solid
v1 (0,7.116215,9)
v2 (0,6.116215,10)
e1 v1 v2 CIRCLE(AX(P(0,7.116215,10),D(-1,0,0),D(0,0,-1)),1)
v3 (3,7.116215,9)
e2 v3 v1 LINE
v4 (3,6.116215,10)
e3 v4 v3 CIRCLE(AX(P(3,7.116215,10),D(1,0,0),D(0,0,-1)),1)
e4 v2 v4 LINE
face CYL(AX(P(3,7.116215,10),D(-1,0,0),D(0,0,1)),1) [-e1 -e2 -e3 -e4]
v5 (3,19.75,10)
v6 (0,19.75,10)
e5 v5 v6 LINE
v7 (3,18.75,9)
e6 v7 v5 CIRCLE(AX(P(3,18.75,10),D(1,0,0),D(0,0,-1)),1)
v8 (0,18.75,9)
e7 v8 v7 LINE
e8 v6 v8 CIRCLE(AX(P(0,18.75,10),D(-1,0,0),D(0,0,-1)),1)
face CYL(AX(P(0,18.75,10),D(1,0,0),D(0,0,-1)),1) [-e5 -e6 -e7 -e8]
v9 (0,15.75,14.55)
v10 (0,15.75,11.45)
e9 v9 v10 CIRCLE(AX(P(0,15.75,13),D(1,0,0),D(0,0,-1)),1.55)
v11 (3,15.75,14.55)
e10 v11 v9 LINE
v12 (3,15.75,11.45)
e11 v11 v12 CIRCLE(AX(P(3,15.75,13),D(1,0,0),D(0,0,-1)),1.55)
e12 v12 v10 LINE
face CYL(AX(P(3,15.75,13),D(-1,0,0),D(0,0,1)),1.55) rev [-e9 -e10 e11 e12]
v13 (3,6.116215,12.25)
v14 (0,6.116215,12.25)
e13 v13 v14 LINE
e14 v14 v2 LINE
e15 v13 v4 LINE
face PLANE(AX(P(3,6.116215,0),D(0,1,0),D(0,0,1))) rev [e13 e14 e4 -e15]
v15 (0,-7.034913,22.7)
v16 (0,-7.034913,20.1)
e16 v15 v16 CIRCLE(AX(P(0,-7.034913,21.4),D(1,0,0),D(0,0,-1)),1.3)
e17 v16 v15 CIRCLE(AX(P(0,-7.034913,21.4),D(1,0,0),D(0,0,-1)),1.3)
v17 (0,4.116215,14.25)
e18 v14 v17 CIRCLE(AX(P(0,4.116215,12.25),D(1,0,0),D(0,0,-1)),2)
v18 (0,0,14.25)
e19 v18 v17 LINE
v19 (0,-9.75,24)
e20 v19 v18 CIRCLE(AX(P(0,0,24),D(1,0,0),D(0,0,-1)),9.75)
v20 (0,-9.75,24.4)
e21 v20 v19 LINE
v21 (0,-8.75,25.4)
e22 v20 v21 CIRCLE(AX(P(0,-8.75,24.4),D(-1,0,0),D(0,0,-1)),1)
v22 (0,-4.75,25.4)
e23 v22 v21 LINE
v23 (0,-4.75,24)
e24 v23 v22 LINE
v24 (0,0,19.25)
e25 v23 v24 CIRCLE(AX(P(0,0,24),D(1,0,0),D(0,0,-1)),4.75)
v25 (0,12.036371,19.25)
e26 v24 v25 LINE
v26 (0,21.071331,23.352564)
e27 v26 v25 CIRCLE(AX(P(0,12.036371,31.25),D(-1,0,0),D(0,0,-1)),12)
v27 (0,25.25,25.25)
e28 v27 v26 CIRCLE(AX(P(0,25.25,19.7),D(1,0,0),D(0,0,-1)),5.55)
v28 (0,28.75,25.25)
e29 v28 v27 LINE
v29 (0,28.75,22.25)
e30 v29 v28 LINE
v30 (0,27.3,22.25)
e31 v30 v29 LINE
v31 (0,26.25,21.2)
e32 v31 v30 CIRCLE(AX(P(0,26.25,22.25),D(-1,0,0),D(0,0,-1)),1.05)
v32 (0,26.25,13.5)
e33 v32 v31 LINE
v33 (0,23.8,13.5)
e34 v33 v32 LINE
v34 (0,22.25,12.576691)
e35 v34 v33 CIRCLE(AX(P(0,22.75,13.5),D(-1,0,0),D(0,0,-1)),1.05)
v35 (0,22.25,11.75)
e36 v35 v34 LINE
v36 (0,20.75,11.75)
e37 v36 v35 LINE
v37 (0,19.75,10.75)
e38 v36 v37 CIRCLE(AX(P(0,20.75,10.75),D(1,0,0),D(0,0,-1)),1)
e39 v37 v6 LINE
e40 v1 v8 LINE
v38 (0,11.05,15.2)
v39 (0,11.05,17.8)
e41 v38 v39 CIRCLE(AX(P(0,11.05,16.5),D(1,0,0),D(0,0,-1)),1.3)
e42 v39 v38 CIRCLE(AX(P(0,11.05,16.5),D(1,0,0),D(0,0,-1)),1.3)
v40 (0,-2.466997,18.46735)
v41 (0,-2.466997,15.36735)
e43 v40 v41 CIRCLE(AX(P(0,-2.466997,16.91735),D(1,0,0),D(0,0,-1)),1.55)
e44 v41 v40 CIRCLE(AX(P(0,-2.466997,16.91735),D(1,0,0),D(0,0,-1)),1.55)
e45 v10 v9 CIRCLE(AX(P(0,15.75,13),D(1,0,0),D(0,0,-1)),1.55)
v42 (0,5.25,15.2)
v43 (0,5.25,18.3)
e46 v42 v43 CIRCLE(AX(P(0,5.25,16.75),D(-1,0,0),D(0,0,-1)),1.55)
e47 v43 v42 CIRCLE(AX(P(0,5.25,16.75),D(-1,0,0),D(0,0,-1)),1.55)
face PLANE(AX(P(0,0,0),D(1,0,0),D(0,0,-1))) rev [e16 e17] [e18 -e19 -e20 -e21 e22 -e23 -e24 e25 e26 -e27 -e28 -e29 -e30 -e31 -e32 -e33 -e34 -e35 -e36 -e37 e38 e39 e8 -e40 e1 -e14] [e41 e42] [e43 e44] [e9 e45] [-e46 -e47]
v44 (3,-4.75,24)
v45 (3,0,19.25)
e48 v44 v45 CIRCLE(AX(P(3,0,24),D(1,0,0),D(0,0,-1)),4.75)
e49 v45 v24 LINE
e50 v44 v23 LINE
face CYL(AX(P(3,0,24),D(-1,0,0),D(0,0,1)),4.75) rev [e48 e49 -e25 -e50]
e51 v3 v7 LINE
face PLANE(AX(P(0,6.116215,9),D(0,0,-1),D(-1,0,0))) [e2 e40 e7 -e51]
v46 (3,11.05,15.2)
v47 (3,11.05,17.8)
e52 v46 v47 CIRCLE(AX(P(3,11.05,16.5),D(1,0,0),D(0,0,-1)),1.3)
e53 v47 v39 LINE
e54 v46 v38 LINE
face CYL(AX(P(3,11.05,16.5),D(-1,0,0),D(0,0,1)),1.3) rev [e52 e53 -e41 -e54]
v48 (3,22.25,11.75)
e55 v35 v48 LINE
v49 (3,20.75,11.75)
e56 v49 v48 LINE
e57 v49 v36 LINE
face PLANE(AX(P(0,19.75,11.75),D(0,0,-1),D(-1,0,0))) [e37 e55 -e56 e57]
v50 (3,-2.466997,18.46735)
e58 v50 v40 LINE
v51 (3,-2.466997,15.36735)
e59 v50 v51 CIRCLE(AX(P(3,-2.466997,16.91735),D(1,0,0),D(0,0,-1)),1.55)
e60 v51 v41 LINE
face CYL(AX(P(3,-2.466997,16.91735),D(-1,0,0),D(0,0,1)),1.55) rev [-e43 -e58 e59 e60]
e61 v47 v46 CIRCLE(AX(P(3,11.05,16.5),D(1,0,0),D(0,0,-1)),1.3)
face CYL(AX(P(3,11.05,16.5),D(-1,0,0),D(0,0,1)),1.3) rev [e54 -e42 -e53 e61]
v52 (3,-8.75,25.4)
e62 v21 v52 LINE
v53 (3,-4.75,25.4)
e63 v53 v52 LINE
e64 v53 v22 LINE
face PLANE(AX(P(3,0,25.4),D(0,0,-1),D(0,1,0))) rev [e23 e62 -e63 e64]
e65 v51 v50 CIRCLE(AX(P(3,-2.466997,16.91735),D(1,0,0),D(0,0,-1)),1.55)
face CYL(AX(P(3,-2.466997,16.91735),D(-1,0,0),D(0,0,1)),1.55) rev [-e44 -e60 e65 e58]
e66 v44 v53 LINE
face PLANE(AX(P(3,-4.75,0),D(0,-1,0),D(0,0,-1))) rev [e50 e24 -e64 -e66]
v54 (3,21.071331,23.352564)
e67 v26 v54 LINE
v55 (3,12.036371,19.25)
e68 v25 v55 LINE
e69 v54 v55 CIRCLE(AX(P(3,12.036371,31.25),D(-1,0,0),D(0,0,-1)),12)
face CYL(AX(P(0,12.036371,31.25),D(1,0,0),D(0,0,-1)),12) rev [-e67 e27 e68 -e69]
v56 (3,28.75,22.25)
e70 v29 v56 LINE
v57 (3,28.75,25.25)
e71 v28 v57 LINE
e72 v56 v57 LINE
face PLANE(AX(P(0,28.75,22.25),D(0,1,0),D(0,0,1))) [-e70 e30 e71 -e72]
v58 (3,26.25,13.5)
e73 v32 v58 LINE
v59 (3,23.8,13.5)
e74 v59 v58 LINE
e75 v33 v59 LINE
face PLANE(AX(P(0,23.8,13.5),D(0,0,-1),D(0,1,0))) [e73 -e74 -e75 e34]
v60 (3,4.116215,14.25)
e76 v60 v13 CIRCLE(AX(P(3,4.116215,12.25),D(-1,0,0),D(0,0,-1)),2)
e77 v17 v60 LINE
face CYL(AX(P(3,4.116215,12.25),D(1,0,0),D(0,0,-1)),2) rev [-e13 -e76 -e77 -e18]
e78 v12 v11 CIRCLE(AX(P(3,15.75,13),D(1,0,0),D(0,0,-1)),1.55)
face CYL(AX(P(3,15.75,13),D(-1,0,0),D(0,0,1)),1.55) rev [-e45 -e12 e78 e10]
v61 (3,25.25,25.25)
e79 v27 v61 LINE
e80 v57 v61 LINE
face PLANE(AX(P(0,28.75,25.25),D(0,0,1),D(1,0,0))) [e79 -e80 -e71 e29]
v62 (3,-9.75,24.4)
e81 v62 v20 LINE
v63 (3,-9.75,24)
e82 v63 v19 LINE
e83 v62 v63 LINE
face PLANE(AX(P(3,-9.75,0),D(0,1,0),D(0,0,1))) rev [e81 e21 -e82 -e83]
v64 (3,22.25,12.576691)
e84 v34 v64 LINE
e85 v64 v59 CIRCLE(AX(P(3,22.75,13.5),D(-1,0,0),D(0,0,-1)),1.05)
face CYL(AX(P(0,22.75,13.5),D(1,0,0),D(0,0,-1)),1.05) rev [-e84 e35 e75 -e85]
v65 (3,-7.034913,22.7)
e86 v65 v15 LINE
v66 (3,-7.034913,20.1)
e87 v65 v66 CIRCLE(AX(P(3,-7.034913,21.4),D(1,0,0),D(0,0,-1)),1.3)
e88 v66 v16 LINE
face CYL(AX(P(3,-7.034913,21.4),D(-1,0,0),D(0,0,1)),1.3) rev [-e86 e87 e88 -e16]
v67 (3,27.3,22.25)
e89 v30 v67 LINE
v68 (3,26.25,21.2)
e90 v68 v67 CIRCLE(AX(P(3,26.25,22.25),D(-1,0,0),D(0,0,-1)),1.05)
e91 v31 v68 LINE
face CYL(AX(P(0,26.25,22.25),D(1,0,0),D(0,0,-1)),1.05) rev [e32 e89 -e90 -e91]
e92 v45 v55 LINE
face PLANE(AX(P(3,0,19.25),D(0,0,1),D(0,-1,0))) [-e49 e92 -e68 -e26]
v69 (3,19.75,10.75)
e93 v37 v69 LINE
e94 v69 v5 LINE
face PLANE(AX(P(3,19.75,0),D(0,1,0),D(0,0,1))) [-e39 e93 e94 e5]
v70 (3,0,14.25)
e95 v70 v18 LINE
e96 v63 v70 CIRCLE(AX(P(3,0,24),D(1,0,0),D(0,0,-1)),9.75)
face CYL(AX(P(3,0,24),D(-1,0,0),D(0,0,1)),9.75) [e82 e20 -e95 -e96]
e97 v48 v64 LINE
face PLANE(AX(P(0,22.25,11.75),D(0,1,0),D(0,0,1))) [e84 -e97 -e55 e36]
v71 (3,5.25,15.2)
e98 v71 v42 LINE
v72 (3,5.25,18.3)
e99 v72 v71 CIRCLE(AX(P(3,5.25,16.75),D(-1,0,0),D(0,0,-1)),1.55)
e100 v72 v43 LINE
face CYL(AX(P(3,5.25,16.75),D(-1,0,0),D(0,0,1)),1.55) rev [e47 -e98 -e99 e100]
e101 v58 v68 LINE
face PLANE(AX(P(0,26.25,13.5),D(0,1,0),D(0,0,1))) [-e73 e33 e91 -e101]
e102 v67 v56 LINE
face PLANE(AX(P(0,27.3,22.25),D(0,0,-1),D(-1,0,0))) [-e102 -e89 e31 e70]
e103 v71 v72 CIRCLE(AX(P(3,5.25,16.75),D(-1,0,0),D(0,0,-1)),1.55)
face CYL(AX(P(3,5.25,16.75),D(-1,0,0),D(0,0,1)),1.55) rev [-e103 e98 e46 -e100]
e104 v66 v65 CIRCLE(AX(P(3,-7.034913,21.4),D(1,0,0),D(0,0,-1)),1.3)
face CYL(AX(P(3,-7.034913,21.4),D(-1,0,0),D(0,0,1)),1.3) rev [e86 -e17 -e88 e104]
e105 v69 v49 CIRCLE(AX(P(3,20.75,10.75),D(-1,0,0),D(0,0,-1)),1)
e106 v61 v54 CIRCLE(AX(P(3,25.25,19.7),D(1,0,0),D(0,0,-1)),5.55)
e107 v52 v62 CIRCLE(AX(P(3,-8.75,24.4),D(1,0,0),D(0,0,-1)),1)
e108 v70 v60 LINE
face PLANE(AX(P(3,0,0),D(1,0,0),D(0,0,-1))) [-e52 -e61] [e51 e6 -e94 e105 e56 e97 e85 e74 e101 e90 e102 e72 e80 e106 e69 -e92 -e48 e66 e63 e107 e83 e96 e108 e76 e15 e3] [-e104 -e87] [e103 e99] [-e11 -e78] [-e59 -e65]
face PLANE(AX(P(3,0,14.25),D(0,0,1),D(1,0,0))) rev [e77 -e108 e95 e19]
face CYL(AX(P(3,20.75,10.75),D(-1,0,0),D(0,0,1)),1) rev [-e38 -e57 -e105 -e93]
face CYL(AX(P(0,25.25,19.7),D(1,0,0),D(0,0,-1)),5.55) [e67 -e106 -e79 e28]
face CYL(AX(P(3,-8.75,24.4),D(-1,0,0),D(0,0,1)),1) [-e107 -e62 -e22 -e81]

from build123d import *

# Parameters (mm, degrees)
SKETCH_1_R      = 1.55
SKETCH_1_R_2    = 1.3
EXTRUDE_1_DEPTH = 3
SKETCH_2_W      = 0.25
SKETCH_2_H      = 13.633784975
EXTRUDE_2_DEPTH = 3
FILLET_R2_1_R   = 2
FILLET_R1_1_R   = 1


with BuildPart() as part:
    # 草图1 → 凸台-拉伸1 (new body)
    with BuildSketch(Plane(origin=(0, 0, 0), x_dir=(0, 0, -1), z_dir=(1, 0, 0))):
        with BuildLine():
            Line((-14.25, 6.116215025), (-9.25, 6.116215025))
            Line((-9.25, 6.116215025), (-9.25, 19.75))
            Line((-9.25, 19.75), (-19.25, 19.75))
            Line((-19.25, 19.75), (-19.25, 0))
            ThreePointArc((-19.25, 0), (-20.641242789, -3.358757211), (-24, -4.75))
            Line((-24, -4.75), (-25.4, -4.75))
            Line((-25.4, -4.75), (-25.4, -9.75))
            Line((-25.4, -9.75), (-24, -9.75))
            ThreePointArc((-24, -9.75), (-17.105708883, -6.894291117), (-14.25, 0))
            Line((-14.25, 0), (-14.25, 6.116215025))
        make_face()
        with Locations((-13, 15.75)):
            Circle(SKETCH_1_R, mode=Mode.SUBTRACT)
        with Locations((-16.75, 5.25)):
            Circle(SKETCH_1_R, mode=Mode.SUBTRACT)
        with Locations((-16.5, 11.05)):
            Circle(SKETCH_1_R_2, mode=Mode.SUBTRACT)
        with Locations((-21.4, -7.034912935)):
            Circle(SKETCH_1_R_2, mode=Mode.SUBTRACT)
        with Locations((-16.917350474, -2.466997302)):
            Circle(SKETCH_1_R, mode=Mode.SUBTRACT)
    extrude(amount=EXTRUDE_1_DEPTH)

    # 草图2 → 凸台-拉伸2 (add, through all)
    with BuildSketch(Plane(origin=(3, 0, 0), x_dir=(0, 0, -1), z_dir=(1, 0, 0))):
        with BuildLine():
            Line((-19.25, 19.75), (-11.75, 19.75))
            Line((-11.75, 19.75), (-11.75, 22.25))
            Line((-11.75, 22.25), (-12.576690734, 22.25))
            ThreePointArc((-12.576690734, 22.25), (-14.402080928, 22.212645368), (-13.5, 23.8))
            Line((-13.5, 23.8), (-13.5, 26.25))
            Line((-13.5, 26.25), (-21.2, 26.25))
            ThreePointArc((-21.2, 26.25), (-22.99246212, 25.50753788), (-22.25, 27.3))
            Line((-22.25, 27.3), (-22.25, 28.75))
            Line((-22.25, 28.75), (-25.25, 28.75))
            Line((-25.25, 28.75), (-25.25, 25.25))
            ThreePointArc((-25.25, 25.25), (-24.753426104, 22.95535741), (-23.352564103, 21.071330896))
            ThreePointArc((-23.352564103, 21.071330896), (-20.323673289, 16.997760056), (-19.25, 12.036370673))
            Line((-19.25, 12.036370673), (-19.25, 19.75))
        make_face()
        with Locations((-9.125, 12.933107513)):
            Rectangle(SKETCH_2_W, SKETCH_2_H)
    extrude(amount=-EXTRUDE_2_DEPTH)

    # R2 圆角1
    fillet_r2_1_edges = [part.edges().sort_by_distance(p)[0] for p in [
        (1.5, 6.116215025, 14.25),
    ]]
    fillet(fillet_r2_1_edges, radius=FILLET_R2_1_R)

    # R1 圆角1
    fillet_r1_1_edges = [part.edges().sort_by_distance(p)[0] for p in [
        (1.5, -9.75, 25.4),
        (1.5, 19.75, 11.75),
        (1.5, 19.75, 9),
        (1.5, 6.116215025, 9),
    ]]
    fillet(fillet_r1_1_edges, radius=FILLET_R1_1_R)


solid = part.part
